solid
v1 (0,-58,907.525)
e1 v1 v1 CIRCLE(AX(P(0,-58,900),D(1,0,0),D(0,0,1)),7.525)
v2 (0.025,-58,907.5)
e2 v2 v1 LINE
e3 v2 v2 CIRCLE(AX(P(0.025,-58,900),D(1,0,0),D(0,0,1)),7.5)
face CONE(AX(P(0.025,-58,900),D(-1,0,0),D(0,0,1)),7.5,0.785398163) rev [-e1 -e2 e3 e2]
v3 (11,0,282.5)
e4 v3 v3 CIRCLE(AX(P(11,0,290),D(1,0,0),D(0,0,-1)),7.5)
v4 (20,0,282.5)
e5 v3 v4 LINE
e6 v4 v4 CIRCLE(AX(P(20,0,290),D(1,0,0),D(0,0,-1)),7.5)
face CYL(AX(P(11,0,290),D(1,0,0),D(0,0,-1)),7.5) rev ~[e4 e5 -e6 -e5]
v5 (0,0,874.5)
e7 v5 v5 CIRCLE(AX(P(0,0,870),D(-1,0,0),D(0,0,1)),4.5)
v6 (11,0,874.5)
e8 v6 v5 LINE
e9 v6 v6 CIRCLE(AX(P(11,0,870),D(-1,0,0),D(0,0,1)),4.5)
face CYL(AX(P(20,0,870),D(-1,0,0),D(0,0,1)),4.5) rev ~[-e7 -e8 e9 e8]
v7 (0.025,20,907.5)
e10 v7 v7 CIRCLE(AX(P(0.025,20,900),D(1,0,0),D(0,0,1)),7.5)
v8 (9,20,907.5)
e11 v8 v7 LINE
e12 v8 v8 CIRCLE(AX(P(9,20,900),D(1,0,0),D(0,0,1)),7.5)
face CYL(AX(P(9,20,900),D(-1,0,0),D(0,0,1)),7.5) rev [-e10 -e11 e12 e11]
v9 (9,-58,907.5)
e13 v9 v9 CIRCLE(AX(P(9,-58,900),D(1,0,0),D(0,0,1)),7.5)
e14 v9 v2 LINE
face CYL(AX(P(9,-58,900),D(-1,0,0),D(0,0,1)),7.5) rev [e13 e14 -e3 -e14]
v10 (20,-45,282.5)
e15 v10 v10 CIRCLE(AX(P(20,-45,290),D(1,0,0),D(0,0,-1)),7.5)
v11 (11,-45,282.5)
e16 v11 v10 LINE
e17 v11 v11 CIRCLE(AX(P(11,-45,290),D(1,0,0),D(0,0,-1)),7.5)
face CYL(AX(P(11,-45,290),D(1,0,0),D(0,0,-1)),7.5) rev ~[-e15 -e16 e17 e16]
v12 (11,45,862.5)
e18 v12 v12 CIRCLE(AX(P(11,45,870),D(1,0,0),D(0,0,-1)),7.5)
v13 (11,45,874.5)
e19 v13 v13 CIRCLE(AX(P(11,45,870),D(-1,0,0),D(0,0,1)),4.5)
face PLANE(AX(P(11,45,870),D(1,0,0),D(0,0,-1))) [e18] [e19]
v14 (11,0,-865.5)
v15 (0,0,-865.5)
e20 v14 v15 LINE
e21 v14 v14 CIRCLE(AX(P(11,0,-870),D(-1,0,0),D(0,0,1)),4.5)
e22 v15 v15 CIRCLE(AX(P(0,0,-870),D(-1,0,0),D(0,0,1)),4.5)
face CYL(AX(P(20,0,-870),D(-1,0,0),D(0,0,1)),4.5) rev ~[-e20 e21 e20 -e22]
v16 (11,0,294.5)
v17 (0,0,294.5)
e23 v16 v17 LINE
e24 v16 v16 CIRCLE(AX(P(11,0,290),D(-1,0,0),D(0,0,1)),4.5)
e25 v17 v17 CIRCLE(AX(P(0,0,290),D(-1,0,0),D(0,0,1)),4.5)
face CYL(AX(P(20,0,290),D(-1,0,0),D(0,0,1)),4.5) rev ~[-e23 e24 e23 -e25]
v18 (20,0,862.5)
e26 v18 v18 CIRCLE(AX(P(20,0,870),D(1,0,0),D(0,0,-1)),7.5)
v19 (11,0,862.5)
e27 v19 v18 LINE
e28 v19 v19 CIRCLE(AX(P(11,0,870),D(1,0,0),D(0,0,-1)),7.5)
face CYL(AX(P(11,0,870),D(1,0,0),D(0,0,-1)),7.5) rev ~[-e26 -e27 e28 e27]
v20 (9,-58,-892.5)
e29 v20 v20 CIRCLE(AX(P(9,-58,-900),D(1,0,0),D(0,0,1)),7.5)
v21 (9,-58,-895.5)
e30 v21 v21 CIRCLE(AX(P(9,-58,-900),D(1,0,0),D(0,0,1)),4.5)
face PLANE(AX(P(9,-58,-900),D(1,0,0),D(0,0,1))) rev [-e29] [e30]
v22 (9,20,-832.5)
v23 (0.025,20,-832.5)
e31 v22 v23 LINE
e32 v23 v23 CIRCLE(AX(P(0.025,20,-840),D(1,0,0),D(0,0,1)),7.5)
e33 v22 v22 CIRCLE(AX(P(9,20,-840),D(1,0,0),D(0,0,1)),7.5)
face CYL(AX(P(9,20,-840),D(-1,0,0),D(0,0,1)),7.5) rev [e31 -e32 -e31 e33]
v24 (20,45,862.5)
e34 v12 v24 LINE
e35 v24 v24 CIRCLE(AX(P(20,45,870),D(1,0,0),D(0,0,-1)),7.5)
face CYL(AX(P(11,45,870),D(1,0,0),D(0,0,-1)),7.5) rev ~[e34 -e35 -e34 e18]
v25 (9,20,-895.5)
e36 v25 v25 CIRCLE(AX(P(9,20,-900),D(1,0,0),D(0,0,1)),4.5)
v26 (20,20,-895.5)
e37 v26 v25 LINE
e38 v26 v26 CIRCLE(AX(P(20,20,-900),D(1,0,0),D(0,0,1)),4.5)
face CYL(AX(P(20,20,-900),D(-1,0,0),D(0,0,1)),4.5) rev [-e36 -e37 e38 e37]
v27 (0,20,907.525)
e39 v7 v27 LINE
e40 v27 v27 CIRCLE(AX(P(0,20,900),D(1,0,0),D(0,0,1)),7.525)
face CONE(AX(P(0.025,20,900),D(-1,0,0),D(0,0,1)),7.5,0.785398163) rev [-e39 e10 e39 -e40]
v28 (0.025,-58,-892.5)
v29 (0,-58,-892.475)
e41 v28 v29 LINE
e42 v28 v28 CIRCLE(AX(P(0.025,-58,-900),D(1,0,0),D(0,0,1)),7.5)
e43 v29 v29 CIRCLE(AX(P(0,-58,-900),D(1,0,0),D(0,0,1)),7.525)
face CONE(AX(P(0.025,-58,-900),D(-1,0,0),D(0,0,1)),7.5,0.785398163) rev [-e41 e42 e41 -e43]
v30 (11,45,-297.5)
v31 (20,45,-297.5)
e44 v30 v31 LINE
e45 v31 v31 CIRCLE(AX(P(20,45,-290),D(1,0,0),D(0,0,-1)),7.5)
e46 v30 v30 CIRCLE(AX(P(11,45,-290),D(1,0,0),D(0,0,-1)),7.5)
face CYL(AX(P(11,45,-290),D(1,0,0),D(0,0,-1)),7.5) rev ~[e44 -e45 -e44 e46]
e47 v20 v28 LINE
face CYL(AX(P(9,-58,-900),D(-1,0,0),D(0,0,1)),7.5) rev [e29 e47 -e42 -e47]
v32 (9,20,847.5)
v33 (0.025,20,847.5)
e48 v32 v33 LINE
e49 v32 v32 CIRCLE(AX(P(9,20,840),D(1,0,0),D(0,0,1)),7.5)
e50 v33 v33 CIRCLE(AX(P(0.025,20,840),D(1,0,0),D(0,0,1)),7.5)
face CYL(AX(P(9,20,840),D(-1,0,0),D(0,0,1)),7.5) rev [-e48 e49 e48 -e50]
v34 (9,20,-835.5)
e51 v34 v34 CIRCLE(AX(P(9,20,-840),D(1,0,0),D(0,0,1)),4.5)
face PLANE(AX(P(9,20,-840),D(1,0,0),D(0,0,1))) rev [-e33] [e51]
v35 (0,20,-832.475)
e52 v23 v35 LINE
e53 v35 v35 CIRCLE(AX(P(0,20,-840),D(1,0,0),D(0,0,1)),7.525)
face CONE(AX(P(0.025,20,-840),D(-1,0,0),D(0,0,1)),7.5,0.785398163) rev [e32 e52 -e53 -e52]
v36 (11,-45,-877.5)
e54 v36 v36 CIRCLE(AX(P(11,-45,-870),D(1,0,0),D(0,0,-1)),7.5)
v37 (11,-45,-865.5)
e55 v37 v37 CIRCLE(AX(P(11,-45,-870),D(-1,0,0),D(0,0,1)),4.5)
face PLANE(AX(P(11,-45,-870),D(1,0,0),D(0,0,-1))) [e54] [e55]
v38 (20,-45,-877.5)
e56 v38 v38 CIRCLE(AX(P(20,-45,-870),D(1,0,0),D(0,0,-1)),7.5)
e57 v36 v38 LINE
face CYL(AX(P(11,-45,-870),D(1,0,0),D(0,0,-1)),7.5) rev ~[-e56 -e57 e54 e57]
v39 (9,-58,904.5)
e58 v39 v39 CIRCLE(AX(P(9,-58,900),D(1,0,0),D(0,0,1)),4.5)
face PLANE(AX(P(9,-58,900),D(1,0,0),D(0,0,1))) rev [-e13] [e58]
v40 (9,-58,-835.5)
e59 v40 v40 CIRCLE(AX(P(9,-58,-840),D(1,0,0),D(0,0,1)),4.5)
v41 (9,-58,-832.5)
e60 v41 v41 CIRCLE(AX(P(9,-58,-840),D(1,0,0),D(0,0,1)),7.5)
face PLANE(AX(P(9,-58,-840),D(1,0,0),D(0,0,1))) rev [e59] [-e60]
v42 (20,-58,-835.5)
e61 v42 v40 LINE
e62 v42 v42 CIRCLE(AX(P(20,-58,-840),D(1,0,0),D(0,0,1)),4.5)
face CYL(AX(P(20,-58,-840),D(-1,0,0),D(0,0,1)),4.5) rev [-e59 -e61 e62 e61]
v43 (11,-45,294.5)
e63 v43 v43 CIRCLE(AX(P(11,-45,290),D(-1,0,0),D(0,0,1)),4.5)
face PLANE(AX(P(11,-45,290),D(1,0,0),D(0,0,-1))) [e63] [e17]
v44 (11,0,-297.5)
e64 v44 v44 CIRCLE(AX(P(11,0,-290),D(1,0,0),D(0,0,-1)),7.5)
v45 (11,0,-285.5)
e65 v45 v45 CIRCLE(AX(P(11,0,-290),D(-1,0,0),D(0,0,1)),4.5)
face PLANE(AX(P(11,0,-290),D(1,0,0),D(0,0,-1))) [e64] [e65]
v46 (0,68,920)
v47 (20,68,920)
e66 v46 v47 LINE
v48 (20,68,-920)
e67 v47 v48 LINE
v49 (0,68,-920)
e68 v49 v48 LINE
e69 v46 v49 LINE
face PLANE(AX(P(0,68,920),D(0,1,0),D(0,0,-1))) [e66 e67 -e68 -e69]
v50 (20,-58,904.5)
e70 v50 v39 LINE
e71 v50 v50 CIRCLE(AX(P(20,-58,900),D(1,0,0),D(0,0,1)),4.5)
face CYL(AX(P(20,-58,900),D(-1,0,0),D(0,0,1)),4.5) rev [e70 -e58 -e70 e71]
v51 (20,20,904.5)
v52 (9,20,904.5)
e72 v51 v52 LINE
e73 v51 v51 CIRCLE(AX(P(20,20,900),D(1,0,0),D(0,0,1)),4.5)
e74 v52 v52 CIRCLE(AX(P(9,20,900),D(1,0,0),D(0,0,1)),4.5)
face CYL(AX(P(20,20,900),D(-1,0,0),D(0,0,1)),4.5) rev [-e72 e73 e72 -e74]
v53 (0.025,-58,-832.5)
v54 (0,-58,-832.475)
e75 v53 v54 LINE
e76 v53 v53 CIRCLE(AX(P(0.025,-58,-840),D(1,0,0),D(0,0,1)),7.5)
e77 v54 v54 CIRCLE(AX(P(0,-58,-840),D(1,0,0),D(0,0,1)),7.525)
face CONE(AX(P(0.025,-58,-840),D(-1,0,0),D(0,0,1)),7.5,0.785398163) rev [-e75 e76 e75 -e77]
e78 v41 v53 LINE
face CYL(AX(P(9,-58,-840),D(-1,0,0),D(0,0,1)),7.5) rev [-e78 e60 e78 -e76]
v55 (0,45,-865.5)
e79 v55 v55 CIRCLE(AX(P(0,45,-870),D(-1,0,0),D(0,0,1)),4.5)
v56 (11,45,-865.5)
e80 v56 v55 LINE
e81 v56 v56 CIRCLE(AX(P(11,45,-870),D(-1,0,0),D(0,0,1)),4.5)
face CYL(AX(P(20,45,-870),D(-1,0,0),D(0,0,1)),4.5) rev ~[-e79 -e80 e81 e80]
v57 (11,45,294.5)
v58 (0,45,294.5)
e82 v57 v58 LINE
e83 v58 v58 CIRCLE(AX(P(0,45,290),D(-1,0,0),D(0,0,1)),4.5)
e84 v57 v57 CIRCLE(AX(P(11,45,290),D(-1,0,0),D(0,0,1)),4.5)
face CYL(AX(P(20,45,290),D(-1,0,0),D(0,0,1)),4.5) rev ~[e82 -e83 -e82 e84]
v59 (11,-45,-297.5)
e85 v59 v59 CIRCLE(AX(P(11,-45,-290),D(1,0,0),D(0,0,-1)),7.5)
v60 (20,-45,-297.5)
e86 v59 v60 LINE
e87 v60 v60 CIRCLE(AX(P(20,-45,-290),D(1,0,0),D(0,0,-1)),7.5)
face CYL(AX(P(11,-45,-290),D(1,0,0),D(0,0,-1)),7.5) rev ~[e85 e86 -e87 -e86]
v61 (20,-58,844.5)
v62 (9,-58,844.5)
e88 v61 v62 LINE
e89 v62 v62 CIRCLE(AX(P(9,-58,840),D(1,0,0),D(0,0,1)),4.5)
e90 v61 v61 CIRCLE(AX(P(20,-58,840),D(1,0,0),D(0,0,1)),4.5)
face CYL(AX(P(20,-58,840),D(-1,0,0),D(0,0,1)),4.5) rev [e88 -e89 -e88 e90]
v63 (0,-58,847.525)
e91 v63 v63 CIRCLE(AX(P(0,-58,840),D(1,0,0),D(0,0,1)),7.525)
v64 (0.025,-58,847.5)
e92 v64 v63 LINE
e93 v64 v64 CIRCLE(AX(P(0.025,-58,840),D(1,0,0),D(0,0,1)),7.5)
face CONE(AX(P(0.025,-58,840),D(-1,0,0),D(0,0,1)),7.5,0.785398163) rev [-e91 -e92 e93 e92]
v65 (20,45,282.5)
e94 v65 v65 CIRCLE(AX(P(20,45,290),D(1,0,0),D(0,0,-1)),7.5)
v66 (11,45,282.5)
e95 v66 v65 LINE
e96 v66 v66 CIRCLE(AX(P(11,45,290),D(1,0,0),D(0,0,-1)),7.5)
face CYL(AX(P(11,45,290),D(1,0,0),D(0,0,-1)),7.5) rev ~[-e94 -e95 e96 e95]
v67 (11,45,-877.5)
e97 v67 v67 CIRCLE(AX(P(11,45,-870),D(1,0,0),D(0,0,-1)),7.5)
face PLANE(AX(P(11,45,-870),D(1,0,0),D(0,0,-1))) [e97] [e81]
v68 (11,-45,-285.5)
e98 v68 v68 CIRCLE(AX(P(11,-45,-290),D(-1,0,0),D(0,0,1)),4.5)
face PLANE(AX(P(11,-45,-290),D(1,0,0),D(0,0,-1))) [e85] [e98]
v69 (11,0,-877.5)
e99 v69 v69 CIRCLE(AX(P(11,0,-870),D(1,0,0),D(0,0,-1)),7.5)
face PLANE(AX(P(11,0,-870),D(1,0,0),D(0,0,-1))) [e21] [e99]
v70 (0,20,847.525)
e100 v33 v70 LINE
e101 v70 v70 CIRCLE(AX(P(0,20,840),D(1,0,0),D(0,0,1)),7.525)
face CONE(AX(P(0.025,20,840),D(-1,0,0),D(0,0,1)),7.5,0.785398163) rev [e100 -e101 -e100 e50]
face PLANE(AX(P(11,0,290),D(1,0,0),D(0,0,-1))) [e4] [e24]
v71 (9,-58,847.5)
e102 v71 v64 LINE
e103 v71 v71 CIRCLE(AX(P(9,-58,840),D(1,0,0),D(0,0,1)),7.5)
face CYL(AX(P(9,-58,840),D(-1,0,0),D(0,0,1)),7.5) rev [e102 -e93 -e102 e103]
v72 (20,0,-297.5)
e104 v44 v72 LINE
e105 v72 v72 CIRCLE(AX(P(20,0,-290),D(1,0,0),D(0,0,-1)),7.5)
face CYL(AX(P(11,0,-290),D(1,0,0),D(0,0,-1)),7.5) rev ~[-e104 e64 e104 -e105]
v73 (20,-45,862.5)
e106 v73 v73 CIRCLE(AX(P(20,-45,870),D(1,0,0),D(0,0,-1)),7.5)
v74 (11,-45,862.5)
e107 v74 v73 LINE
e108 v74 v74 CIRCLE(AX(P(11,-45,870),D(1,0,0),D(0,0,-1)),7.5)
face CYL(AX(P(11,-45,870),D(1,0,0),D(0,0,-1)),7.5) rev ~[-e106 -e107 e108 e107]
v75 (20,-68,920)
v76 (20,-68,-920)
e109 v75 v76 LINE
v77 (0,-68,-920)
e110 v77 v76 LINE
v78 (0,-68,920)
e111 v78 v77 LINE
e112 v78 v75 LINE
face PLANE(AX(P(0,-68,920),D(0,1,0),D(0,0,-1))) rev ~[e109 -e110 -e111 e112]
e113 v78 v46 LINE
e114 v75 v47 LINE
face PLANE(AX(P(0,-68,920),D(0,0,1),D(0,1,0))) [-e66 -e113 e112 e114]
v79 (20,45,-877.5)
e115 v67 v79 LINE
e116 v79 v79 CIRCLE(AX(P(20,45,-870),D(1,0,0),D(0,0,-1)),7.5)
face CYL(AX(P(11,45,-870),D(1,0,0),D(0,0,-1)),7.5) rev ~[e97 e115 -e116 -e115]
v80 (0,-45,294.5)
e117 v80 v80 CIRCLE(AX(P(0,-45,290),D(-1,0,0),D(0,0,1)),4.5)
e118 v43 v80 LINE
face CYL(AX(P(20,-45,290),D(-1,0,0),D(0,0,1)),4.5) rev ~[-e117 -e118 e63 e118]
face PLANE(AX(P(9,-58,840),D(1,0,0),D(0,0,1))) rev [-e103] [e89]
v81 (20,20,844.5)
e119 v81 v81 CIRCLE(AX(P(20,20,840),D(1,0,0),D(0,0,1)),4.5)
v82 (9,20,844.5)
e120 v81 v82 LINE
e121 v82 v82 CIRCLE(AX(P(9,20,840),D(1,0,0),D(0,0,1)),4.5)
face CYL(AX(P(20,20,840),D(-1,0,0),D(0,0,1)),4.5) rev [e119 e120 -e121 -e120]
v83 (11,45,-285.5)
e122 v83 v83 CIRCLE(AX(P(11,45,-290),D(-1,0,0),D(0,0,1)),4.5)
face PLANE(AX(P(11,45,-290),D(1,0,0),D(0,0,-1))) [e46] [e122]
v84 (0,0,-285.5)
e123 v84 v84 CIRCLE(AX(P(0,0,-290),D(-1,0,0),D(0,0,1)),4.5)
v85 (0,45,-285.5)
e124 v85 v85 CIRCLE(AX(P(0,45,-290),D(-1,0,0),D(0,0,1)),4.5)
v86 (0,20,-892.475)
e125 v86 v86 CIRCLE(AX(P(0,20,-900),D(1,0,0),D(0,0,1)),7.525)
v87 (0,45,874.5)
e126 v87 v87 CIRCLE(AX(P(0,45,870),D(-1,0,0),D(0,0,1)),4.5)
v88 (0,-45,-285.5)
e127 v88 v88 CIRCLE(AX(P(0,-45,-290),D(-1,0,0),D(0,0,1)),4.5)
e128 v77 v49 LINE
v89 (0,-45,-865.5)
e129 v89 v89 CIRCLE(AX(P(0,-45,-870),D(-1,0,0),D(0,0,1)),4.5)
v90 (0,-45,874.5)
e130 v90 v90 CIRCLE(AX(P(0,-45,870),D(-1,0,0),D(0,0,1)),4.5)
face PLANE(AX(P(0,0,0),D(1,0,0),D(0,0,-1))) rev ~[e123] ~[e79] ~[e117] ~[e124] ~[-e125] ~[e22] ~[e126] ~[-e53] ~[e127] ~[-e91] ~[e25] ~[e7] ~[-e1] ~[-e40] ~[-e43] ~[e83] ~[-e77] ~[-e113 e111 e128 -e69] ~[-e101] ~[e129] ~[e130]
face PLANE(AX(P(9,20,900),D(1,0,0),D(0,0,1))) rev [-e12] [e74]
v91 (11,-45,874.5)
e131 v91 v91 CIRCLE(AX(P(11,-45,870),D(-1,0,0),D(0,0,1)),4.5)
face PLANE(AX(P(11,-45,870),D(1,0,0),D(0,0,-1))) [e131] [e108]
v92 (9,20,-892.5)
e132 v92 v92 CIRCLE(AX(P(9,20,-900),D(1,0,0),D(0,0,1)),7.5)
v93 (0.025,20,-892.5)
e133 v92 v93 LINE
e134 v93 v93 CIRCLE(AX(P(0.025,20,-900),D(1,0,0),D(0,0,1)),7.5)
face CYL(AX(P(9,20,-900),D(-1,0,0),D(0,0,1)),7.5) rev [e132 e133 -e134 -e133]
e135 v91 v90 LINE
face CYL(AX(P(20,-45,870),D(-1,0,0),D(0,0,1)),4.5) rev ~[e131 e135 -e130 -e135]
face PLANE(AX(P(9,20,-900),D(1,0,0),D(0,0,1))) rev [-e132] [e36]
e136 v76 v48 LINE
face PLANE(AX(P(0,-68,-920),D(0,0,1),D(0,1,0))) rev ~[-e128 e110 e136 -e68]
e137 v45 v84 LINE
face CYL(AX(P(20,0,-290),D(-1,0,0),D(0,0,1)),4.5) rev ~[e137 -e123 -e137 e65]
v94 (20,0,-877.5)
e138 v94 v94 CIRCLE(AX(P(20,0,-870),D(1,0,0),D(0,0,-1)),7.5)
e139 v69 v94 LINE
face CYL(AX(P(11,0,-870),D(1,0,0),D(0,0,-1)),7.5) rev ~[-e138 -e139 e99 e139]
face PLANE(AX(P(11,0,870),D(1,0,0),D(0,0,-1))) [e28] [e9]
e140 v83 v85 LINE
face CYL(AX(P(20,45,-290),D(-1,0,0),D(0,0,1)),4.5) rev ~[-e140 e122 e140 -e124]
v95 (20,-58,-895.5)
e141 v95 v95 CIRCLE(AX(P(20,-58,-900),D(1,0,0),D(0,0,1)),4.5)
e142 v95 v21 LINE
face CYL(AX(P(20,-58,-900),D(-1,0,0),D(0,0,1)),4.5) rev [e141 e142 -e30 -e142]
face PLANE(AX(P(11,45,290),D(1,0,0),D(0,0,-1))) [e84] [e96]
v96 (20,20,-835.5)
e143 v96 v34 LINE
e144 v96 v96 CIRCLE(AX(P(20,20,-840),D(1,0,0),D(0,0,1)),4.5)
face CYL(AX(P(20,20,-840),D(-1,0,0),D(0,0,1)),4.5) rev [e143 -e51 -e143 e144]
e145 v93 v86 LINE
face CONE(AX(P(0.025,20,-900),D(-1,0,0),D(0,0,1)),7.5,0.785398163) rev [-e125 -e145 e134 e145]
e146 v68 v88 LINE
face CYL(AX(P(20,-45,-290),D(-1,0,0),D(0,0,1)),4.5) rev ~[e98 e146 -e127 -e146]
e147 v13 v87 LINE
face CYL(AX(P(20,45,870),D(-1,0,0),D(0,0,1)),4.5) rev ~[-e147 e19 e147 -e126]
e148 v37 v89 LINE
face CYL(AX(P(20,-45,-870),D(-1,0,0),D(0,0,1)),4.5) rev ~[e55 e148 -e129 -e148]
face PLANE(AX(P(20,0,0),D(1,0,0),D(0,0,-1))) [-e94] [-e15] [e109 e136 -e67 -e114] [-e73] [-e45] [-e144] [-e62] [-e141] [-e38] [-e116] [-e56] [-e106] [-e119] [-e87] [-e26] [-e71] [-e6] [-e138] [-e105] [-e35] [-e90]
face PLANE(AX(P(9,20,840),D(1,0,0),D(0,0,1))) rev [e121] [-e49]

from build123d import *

# Parameters (mm, degrees)
SKETCH_2_W                 = 1840
SKETCH_2_H                 = 136
EXTRUDE_2_DEPTH            = 20
HOLE_WIZARD_2_D            = 9
HOLE_WIZARD_2_CBORE_D      = 15
HOLE_WIZARD_2_CBORE_DEPTH  = 9
PATTERN_LINEAR_1_COUNT     = 4
PATTERN_LINEAR_1_PITCH     = 580
HOLE_WIZARD_2_2_AT_2_COUNT = 2
HOLE_WIZARD_2_2_AT_2_PITCH = 60
HOLE_WIZARD_2_2_AT_3_COUNT = 2
HOLE_WIZARD_2_2_AT_3_PITCH = 78
HOLE_WIZARD_2_2_AT_4_COUNT = 2
HOLE_WIZARD_2_2_AT_4_PITCH = 98.407316801
HOLE_WIZARD_2_2_AT_5_COUNT = 2
HOLE_WIZARD_2_2_AT_5_PITCH = 1740
HOLE_WIZARD_2_2_AT_6_COUNT = 2
HOLE_WIZARD_2_2_AT_6_PITCH = 1800
HOLE_WIZARD_2_2_AT_7_COUNT = 2
HOLE_WIZARD_2_2_AT_7_PITCH = 1741.747398448
HOLE_WIZARD_2_2_AT_8_COUNT = 2
HOLE_WIZARD_2_2_AT_8_PITCH = 1801.689207383


with BuildPart() as part:
    # 草图2 → 凸台-拉伸2 (new body)
    with BuildSketch(Plane(origin=(0, 0, 0), x_dir=(0, 0, -1), z_dir=(1, 0, 0))):
        Rectangle(SKETCH_2_W, SKETCH_2_H)
    extrude(amount=EXTRUDE_2_DEPTH)

    # Hole Wizard 2 (through all)
    with Locations(Plane(origin=(20, 0, 0), x_dir=(0, 0, -1), z_dir=(1, 0, 0))):
        with Locations((-870, 45), (-870, -45), (-870, 0)):
            hole_wizard_2 = CounterBoreHole(HOLE_WIZARD_2_D / 2, HOLE_WIZARD_2_CBORE_D / 2, HOLE_WIZARD_2_CBORE_DEPTH)

    # 阵列(线性)1: Hole Wizard 2 ×4
    with Locations(*[(0, 0, -i * PATTERN_LINEAR_1_PITCH) for i in range(1, PATTERN_LINEAR_1_COUNT)]):
        add(hole_wizard_2, mode=Mode.SUBTRACT)

    # 草图6 → Hole Wizard 2 2 (revolve, cut)
    with BuildSketch(Plane(origin=(0, 20, -900), x_dir=(0, 0, 1), z_dir=(0, 1, 0))):
        Polygon((0, 0), (0, 20), (4.5, 20), (4.5, 9), (7.5, 9), (7.5, 0.025), (7.525, 0), align=None)
    hole_wizard_2_2 = revolve(axis=Axis((-6.35, 20, -900), (1, 0, 0)), mode=Mode.SUBTRACT)

    # Hole Wizard 2 2 at 2: Hole Wizard 2 2 ×2
    with Locations(*[(0, 0, i * HOLE_WIZARD_2_2_AT_2_PITCH) for i in range(1, HOLE_WIZARD_2_2_AT_2_COUNT)]):
        add(hole_wizard_2_2, mode=Mode.SUBTRACT)

    # Hole Wizard 2 2 at 3: Hole Wizard 2 2 ×2
    with Locations(*[(0, -i * HOLE_WIZARD_2_2_AT_3_PITCH, 0) for i in range(1, HOLE_WIZARD_2_2_AT_3_COUNT)]):
        add(hole_wizard_2_2, mode=Mode.SUBTRACT)

    # Hole Wizard 2 2 at 4: Hole Wizard 2 2 ×2
    with Locations(*[Vector(0, -0.7926239891046006, 0.6097107608496917) * (i * HOLE_WIZARD_2_2_AT_4_PITCH) for i in range(1, HOLE_WIZARD_2_2_AT_4_COUNT)]):
        add(hole_wizard_2_2, mode=Mode.SUBTRACT)

    # Hole Wizard 2 2 at 5: Hole Wizard 2 2 ×2
    with Locations(*[(0, 0, i * HOLE_WIZARD_2_2_AT_5_PITCH) for i in range(1, HOLE_WIZARD_2_2_AT_5_COUNT)]):
        add(hole_wizard_2_2, mode=Mode.SUBTRACT)

    # Hole Wizard 2 2 at 6: Hole Wizard 2 2 ×2
    with Locations(*[(0, 0, i * HOLE_WIZARD_2_2_AT_6_PITCH) for i in range(1, HOLE_WIZARD_2_2_AT_6_COUNT)]):
        add(hole_wizard_2_2, mode=Mode.SUBTRACT)

    # Hole Wizard 2 2 at 7: Hole Wizard 2 2 ×2
    with Locations(*[Vector(0, -0.0447826131788728, 0.9989967555287012) * (i * HOLE_WIZARD_2_2_AT_7_PITCH) for i in range(1, HOLE_WIZARD_2_2_AT_7_COUNT)]):
        add(hole_wizard_2_2, mode=Mode.SUBTRACT)

    # Hole Wizard 2 2 at 8: Hole Wizard 2 2 ×2
    with Locations(*[Vector(0, -0.04329270535693645, 0.9990624313139183) * (i * HOLE_WIZARD_2_2_AT_8_PITCH) for i in range(1, HOLE_WIZARD_2_2_AT_8_COUNT)]):
        add(hole_wizard_2_2, mode=Mode.SUBTRACT)


solid = part.part
